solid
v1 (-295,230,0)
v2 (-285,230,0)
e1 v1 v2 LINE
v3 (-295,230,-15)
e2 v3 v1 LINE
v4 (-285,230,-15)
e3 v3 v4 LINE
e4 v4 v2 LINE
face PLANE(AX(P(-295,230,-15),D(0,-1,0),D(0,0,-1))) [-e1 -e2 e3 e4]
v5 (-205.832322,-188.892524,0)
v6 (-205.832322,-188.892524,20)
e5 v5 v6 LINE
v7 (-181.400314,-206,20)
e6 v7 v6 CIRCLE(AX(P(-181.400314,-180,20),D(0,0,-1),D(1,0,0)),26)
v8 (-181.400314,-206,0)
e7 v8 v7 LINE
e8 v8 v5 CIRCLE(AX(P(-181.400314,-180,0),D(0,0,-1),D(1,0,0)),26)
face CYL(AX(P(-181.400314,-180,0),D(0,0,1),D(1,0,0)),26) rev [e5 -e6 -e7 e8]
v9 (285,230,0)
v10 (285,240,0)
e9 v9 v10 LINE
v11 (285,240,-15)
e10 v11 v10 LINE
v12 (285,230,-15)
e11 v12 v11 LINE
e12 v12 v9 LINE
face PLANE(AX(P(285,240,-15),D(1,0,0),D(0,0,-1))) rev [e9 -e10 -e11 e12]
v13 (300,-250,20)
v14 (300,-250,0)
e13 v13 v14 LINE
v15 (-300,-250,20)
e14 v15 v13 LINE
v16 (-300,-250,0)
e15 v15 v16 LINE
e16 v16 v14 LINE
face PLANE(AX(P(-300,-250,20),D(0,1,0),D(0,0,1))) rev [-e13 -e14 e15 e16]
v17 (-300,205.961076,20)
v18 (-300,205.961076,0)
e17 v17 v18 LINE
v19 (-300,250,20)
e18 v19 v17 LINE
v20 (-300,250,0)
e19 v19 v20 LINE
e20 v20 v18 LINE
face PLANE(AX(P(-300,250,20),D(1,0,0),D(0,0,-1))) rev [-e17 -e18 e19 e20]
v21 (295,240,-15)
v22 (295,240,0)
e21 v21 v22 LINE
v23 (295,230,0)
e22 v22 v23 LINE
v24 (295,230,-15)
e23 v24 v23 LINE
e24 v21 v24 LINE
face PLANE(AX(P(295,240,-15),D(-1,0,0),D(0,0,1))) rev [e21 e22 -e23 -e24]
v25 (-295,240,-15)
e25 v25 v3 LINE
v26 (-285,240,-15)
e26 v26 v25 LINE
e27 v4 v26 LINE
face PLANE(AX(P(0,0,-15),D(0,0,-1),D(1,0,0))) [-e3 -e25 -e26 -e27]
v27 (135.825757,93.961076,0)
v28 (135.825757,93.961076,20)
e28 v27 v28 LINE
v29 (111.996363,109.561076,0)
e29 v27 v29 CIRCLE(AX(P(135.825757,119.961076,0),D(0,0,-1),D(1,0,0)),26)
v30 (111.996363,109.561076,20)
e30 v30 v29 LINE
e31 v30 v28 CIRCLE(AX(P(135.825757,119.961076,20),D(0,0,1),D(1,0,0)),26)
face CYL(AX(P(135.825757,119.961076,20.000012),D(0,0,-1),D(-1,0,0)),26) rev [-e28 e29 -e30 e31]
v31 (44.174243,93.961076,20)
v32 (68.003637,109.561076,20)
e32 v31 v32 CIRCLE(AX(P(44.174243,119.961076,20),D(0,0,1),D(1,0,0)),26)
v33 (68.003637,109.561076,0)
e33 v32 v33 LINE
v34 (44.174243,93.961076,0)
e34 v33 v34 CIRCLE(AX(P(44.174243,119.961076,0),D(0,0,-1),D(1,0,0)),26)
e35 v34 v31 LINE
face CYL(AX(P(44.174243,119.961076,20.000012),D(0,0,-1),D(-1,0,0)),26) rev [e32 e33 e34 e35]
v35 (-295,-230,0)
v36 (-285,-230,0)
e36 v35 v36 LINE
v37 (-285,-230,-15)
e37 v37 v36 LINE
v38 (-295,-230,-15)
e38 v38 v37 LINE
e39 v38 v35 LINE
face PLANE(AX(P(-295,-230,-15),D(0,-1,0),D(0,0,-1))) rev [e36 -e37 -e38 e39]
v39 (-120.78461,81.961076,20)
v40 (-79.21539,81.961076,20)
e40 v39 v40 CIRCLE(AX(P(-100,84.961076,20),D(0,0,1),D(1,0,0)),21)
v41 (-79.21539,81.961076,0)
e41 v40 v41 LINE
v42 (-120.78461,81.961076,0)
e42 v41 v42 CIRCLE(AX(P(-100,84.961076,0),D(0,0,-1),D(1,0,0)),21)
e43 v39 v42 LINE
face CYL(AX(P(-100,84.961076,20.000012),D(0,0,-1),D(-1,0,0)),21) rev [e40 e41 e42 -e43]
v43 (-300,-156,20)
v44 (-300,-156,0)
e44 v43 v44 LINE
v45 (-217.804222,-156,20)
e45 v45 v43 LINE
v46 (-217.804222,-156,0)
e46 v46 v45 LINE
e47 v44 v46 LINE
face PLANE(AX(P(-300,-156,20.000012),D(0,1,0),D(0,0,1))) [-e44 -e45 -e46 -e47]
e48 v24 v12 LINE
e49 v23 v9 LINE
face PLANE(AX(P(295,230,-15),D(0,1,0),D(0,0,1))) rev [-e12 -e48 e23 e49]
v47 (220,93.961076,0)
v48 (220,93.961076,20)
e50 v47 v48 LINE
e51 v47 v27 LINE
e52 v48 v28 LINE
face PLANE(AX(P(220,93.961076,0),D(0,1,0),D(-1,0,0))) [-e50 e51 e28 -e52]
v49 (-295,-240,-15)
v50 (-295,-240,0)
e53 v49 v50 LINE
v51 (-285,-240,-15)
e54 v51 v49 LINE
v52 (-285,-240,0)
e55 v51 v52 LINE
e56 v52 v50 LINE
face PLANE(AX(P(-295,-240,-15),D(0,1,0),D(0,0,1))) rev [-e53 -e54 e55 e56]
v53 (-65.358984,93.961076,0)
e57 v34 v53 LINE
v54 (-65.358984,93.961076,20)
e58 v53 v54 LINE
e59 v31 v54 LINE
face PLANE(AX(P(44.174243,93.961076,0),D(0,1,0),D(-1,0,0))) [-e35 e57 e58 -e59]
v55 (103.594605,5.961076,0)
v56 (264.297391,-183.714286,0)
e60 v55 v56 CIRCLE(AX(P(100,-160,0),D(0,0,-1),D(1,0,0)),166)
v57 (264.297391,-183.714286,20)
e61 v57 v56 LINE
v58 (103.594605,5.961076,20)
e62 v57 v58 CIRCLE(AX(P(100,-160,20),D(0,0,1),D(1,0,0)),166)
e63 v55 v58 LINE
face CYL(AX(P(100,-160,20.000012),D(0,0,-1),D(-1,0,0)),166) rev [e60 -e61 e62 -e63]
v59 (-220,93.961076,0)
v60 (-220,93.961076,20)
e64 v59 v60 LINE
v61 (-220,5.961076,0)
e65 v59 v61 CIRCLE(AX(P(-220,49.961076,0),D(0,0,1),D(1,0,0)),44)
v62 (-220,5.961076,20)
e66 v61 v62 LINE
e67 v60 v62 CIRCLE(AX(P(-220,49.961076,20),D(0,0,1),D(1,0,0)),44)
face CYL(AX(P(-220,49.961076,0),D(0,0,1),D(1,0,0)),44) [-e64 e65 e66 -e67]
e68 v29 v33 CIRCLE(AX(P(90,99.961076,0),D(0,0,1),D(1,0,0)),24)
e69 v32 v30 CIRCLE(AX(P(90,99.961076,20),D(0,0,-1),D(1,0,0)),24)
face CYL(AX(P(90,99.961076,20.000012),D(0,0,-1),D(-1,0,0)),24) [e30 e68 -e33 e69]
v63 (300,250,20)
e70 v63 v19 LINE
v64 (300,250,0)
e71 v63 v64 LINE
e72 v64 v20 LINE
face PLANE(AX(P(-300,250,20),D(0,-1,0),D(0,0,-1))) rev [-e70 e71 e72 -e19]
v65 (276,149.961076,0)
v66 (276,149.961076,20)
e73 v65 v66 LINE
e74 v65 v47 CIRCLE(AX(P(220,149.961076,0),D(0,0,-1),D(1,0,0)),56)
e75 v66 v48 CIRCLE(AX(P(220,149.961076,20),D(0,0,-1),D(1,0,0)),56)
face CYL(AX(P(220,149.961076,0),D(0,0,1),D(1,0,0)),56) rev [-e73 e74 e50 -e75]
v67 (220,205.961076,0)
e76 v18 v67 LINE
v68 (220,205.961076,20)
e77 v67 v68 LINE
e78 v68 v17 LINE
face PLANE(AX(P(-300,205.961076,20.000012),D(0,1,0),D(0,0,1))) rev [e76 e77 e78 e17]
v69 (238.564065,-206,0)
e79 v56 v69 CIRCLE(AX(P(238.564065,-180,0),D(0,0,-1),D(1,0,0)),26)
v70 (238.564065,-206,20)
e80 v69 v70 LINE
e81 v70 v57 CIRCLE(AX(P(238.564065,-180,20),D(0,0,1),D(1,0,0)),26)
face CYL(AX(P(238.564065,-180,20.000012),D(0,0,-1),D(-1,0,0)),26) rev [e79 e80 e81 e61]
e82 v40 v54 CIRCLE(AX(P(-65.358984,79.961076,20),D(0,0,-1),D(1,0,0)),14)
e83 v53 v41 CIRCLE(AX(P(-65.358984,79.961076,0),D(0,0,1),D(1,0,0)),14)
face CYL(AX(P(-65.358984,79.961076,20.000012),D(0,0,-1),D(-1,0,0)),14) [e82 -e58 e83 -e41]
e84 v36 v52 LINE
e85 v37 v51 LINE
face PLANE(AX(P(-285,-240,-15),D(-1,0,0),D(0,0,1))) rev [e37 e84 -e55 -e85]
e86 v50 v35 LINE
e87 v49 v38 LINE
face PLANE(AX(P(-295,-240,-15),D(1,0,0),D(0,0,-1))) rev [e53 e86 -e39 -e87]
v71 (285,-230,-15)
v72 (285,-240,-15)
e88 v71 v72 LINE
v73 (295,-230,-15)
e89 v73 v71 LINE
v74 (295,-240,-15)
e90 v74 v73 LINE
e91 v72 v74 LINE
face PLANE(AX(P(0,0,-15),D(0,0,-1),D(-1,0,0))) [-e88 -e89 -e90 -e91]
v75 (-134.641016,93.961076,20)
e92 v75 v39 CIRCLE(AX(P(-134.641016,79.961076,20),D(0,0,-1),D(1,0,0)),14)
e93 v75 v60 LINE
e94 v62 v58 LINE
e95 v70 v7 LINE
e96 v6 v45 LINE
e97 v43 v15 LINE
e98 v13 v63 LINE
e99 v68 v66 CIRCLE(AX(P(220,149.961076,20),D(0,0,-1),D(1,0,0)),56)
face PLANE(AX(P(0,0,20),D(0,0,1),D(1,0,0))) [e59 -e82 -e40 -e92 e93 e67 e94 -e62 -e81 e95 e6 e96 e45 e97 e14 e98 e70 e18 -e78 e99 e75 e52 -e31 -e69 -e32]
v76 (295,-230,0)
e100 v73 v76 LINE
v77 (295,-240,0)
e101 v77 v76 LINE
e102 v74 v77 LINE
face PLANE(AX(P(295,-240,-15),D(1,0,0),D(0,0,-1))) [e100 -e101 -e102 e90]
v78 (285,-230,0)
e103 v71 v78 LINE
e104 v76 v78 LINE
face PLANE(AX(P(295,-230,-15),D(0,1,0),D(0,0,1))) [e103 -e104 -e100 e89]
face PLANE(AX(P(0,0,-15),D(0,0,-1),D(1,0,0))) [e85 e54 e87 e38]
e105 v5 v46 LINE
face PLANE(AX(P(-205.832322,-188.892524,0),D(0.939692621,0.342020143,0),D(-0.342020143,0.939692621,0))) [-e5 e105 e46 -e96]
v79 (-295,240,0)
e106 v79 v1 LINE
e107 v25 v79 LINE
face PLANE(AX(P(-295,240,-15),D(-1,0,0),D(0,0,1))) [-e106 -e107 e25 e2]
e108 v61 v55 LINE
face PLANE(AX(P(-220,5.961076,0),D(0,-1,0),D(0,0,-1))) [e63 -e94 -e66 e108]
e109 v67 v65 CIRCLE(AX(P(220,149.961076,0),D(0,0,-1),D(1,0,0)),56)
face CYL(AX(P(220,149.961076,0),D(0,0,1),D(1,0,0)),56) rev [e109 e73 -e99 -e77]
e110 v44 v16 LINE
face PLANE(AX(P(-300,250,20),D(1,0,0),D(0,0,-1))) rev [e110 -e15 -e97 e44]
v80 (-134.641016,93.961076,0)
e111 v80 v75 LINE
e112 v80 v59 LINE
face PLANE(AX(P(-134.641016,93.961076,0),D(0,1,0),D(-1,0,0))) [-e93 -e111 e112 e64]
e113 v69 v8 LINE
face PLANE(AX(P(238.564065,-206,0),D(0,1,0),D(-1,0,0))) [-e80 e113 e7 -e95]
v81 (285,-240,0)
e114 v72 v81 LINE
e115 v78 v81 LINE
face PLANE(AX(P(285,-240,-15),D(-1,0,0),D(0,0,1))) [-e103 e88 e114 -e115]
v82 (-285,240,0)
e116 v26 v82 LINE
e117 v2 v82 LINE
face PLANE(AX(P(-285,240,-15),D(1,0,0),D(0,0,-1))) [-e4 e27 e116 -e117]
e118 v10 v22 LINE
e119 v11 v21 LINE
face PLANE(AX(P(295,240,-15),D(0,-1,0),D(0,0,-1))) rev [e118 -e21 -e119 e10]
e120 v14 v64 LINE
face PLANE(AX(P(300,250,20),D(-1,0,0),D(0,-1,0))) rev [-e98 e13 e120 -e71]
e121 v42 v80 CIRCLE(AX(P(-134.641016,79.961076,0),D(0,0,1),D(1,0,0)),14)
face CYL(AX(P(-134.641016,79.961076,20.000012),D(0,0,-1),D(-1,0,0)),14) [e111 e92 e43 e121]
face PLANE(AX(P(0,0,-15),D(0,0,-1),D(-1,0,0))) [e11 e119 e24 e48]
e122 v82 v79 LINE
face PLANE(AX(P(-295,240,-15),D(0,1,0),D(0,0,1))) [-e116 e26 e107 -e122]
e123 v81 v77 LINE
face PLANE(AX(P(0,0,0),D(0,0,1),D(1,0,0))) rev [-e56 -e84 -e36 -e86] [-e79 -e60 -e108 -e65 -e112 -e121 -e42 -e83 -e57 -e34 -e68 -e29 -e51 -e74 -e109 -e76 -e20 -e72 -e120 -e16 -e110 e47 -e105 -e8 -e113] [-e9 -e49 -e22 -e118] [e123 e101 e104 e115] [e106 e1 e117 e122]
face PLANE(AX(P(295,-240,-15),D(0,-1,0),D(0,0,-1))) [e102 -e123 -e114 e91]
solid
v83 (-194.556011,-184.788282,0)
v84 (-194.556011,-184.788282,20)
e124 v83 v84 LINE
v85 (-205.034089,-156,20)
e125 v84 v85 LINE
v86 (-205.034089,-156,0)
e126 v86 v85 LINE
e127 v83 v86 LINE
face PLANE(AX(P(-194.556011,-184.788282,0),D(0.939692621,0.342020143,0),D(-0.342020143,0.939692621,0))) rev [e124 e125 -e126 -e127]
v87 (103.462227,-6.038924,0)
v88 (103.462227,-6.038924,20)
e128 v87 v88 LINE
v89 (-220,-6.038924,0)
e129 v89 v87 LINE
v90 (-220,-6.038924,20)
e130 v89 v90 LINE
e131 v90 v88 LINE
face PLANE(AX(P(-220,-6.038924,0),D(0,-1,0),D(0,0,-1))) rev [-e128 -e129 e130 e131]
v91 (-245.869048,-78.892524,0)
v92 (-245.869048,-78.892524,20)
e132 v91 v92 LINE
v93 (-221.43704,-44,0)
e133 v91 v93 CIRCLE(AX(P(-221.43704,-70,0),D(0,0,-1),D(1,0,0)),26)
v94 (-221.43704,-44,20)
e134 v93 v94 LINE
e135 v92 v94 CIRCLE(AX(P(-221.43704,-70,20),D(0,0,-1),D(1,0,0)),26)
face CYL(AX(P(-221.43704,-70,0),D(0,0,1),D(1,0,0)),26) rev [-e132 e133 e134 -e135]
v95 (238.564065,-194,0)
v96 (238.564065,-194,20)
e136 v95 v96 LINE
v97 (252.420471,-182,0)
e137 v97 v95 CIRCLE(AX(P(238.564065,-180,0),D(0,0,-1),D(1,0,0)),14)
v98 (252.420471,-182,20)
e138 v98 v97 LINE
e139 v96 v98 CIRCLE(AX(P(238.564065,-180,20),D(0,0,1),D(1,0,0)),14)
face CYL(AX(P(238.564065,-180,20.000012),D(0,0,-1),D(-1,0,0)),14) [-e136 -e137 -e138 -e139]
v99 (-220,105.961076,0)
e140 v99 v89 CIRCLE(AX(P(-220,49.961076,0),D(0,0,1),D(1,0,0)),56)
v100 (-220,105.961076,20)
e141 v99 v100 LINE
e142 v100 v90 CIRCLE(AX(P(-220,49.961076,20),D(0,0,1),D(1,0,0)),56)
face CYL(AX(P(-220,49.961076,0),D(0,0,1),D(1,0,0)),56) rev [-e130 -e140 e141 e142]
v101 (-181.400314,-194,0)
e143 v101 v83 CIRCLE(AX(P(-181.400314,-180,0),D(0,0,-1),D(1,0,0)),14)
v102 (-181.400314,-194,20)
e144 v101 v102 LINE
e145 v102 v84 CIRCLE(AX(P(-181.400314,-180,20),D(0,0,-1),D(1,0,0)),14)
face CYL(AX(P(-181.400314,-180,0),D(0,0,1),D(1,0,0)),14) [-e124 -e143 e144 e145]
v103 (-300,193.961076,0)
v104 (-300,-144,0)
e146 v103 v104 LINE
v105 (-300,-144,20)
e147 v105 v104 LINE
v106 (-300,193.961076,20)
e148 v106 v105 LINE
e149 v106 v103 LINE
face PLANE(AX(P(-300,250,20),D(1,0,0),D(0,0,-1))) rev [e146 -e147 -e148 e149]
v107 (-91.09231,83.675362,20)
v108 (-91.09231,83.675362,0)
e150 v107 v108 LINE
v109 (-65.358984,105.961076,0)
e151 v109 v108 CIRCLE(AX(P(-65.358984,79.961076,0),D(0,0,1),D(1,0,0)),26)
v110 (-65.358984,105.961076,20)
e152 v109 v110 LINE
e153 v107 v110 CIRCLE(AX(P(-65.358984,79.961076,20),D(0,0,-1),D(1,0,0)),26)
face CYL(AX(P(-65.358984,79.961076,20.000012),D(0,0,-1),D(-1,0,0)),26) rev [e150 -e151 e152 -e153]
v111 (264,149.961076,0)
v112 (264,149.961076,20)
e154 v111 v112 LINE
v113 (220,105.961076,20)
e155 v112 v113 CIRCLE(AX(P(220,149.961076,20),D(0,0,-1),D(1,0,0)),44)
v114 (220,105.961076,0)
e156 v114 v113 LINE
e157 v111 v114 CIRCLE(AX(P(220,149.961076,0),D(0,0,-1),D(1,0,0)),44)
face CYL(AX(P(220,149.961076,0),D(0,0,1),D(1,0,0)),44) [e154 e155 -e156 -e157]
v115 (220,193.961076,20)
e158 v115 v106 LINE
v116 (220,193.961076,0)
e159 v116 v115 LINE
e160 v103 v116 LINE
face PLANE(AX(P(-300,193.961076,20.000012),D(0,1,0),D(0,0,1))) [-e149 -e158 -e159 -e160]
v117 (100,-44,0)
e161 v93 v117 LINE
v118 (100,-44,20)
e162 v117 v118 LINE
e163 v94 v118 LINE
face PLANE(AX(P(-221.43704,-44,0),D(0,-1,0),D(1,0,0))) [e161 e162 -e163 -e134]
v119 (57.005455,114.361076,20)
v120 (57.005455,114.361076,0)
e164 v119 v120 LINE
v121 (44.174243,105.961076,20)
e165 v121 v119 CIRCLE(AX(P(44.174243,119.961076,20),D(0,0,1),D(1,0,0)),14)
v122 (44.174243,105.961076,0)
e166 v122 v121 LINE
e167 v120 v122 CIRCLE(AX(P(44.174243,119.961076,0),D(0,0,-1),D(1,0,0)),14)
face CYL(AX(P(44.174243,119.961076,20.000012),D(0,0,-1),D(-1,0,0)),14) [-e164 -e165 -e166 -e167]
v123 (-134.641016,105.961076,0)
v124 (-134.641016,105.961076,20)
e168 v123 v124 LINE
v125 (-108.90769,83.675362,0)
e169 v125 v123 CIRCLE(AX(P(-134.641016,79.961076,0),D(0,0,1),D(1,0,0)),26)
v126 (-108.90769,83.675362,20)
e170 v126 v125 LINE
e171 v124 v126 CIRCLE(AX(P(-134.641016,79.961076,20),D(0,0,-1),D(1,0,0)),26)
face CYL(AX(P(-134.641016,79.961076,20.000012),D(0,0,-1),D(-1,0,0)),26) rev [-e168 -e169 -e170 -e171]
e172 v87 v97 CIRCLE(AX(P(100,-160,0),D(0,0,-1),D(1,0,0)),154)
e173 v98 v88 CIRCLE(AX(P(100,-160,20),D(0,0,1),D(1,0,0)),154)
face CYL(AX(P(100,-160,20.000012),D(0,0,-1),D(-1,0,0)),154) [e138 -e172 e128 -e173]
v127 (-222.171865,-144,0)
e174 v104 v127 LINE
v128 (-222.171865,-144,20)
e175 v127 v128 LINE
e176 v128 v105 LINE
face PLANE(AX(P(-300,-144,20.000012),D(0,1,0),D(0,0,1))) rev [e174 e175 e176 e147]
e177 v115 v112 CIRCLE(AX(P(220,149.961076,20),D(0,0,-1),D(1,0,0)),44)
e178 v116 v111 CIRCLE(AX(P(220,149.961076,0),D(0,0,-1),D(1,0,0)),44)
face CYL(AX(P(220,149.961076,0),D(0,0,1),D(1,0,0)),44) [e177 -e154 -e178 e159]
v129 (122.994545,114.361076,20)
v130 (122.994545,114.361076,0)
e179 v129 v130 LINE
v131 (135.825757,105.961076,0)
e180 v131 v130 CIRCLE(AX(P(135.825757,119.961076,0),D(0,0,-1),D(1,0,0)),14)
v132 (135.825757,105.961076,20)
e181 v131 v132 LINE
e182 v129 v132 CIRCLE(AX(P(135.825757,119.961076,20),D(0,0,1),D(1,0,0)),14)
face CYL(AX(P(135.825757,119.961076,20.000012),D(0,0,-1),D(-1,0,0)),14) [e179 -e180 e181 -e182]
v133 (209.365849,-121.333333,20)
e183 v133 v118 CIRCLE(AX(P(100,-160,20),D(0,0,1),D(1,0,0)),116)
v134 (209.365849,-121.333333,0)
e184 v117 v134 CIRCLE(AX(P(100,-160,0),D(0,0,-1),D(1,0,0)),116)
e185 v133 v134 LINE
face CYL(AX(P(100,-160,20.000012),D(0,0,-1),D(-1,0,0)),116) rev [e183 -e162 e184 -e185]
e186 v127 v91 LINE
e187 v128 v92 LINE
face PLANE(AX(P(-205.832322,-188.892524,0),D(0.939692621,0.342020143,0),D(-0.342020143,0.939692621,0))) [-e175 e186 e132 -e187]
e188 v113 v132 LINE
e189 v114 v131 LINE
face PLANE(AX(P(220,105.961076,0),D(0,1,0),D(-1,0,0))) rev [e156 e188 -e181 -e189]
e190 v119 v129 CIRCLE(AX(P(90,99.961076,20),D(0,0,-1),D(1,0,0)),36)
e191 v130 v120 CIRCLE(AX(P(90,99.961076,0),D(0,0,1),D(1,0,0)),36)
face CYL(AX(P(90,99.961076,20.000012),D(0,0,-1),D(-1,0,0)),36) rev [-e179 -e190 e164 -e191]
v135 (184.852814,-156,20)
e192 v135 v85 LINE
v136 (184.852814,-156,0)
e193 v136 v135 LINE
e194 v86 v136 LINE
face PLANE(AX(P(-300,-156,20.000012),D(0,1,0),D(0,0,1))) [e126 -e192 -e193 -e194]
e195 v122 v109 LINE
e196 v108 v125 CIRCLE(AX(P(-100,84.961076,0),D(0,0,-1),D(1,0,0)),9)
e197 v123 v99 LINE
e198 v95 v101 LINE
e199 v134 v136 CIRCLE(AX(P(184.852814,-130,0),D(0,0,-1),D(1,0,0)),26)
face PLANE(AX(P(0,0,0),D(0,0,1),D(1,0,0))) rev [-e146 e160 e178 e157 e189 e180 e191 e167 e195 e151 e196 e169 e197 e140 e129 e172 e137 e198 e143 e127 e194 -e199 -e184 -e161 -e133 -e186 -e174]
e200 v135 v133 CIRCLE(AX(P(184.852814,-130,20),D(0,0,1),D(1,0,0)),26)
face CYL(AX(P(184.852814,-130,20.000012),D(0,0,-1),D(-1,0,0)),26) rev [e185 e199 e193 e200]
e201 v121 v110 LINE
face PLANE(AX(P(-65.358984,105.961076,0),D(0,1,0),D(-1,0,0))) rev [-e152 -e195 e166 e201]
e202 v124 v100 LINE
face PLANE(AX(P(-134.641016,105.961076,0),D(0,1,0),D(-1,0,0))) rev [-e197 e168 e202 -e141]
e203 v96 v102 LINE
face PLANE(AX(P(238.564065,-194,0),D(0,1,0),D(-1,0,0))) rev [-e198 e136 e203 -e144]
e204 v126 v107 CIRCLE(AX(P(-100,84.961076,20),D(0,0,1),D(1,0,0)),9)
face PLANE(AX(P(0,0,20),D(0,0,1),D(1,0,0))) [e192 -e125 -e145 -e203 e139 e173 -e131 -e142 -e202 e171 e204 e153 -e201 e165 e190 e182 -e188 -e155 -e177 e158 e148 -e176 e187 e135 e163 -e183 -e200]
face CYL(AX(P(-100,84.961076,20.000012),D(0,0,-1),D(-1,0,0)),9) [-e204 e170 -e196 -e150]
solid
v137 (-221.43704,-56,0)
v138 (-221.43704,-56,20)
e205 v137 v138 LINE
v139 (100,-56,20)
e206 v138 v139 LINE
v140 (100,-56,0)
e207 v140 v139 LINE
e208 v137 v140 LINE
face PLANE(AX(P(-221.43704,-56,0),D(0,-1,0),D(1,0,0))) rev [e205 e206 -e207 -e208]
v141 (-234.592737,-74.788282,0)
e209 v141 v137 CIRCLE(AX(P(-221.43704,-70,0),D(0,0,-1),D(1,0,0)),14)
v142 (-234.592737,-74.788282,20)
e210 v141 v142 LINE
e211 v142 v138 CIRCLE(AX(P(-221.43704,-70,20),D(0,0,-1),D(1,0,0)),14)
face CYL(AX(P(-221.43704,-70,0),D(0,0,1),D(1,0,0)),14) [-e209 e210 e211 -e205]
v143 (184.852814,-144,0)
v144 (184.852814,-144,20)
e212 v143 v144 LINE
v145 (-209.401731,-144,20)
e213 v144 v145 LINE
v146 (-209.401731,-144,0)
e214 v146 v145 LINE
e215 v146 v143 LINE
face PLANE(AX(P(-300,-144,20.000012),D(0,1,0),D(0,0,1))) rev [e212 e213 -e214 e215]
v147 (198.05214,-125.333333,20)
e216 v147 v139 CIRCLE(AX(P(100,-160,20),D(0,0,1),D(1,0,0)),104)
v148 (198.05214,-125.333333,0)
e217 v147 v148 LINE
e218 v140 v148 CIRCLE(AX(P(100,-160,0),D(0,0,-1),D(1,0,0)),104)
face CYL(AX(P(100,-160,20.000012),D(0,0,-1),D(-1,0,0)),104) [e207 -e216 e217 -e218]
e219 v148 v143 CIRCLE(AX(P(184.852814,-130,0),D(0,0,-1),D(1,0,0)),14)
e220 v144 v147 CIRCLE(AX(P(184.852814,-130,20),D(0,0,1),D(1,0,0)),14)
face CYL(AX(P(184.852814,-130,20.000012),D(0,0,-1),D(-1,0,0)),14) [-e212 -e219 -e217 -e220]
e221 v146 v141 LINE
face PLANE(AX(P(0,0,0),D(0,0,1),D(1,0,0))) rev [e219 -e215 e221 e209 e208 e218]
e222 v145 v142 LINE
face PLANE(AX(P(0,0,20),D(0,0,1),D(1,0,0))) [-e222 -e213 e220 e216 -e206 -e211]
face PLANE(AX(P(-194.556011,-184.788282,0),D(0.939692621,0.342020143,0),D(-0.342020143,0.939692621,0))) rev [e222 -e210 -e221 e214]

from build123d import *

# Parameters (mm, degrees)
SKETCH1_W                    = 600
SKETCH1_H                    = 500
BOSS_EXTRUDE1_DEPTH          = 20
CUT_EXTRUDE_THIN1_DEPTH      = 392.02429592
CUT_EXTRUDE_THIN1_DEPTH_BACK = 20
CUT_EXTRUDE_THIN2_DEPTH      = 392.02429592
CUT_EXTRUDE_THIN2_DEPTH_BACK = 20
SKETCH3_W                    = 484.852813742
SKETCH3_H                    = 12
SKETCH4_W                    = 10
SKETCH4_H                    = 10
BOSS_EXTRUDE2_DEPTH          = 15
MIRROR2_COPY_1_SKETCH_W      = 10
MIRROR2_COPY_1_SKETCH_H      = 10
MIRROR2_COPY_1_DEPTH         = 15


with BuildPart() as part:
    # Sketch1 → Boss-Extrude1 (new body)
    with BuildSketch(Plane.XY):
        Rectangle(SKETCH1_W, SKETCH1_H)
    extrude(amount=BOSS_EXTRUDE1_DEPTH)

    # Sketch2 → Cut-Extrude-Thin1 (cut, two sides: drawn at the far end of the back side and taken through both)
    with BuildSketch(Plane.XY.offset(20).offset(-CUT_EXTRUDE_THIN1_DEPTH_BACK)):
        with BuildLine():
            Line((-300, 193.961076205), (220, 193.961076205))
            ThreePointArc((220, 193.961076205), (264, 149.961076205), (220, 105.961076205))
            Line((220, 105.961076205), (135.82575695, 105.961076205))
            ThreePointArc((135.82575695, 105.961076205), (128.157641144, 108.247835834), (122.994545004, 114.361076205))
            ThreePointArc((122.994545004, 114.361076205), (90, 135.961076205), (57.005454996, 114.361076205))
            ThreePointArc((57.005454996, 114.361076205), (51.842358856, 108.247835834), (44.17424305, 105.961076205))
            Line((44.17424305, 105.961076205), (-2.040587873, 105.961076205))
            Line((-2.040587873, 105.961076205), (-65.358983849, 105.961076205))
            ThreePointArc((-65.358983849, 105.961076205), (-82.379979287, 99.615228802), (-91.092310133, 83.675361919))
            ThreePointArc((-91.092310133, 83.675361919), (-100, 75.961076205), (-108.907689867, 83.675361919))
            ThreePointArc((-108.907689867, 83.675361919), (-117.620020713, 99.615228802), (-134.641016151, 105.961076205))
            Line((-134.641016151, 105.961076205), (-220, 105.961076205))
            ThreePointArc((-220, 105.961076205), (-276, 49.961076205), (-220, -6.038923795))
            Line((-220, -6.038923795), (103.462226705, -6.038923795))
            ThreePointArc((103.462226705, -6.038923795), (217.539052876, -60.498386701), (252.420471066, -182))
            ThreePointArc((252.420471066, -182), (247.729215995, -190.583005244), (238.564064606, -194))
            Line((238.564064606, -194), (-181.400314096, -194))
            ThreePointArc((-181.400314096, -194), (-189.430384205, -191.46812862), (-194.556010787, -184.788282007))
            Line((-194.556010787, -184.788282007), (-234.592736556, -74.788282007))
            ThreePointArc((-234.592736556, -74.788282007), (-232.905168485, -61.969929891), (-221.437039865, -56))
            Line((-221.437039865, -56), (100, -56))
            ThreePointArc((100, -56), (160.044427996, -75.084355584), (198.052140325, -125.333333333))
            ThreePointArc((198.052140325, -125.333333333), (196.283765875, -138.082903769), (184.852813742, -144))
            Line((184.852813742, -144), (184.852813742, -156))
            ThreePointArc((184.852813742, -156), (206.081724847, -145.011106999), (209.365848824, -121.333333333))
            ThreePointArc((209.365848824, -121.333333333), (166.972631226, -65.286396612), (100, -44))
            Line((100, -44), (-221.437039865, -44))
            ThreePointArc((-221.437039865, -44), (-242.734993017, -55.087012655), (-245.869048006, -78.892523726))
            Line((-245.869048006, -78.892523726), (-205.832322236, -188.892523726))
            ThreePointArc((-205.832322236, -188.892523726), (-196.313301441, -201.297953152), (-181.400314096, -206))
            Line((-181.400314096, -206), (238.564064606, -206))
            ThreePointArc((238.564064606, -206), (255.585060044, -199.654152596), (264.297390889, -183.714285714))
            ThreePointArc((264.297390889, -183.714285714), (226.653528564, -52.692573871), (103.594604963, 5.961076205))
            Line((103.594604963, 5.961076205), (-220, 5.961076205))
            ThreePointArc((-220, 5.961076205), (-264, 49.961076205), (-220, 93.961076205))
            Line((-220, 93.961076205), (-134.641016151, 93.961076205))
            ThreePointArc((-134.641016151, 93.961076205), (-125.475864761, 90.544081449), (-120.784609691, 81.961076205))
            ThreePointArc((-120.784609691, 81.961076205), (-100, 63.961076205), (-79.215390309, 81.961076205))
            ThreePointArc((-79.215390309, 81.961076205), (-74.524135239, 90.544081449), (-65.358983849, 93.961076205))
            Line((-65.358983849, 93.961076205), (-2.040587873, 93.961076205))
            Line((-2.040587873, 93.961076205), (44.17424305, 93.961076205))
            ThreePointArc((44.17424305, 93.961076205), (58.415029546, 98.207915515), (68.003636664, 109.561076205))
            ThreePointArc((68.003636664, 109.561076205), (90, 123.961076205), (111.996363336, 109.561076205))
            ThreePointArc((111.996363336, 109.561076205), (121.584970454, 98.207915515), (135.82575695, 93.961076205))
            Line((135.82575695, 93.961076205), (220, 93.961076205))
            ThreePointArc((220, 93.961076205), (276, 149.961076205), (220, 205.961076205))
            Line((220, 205.961076205), (-300, 205.961076205))
            Line((-300, 205.961076205), (-300, 193.961076205))
        make_face()
    extrude(amount=CUT_EXTRUDE_THIN1_DEPTH + CUT_EXTRUDE_THIN1_DEPTH_BACK, mode=Mode.SUBTRACT)

    # Sketch3 → Cut-Extrude-Thin2 (cut, two sides: drawn at the far end of the back side and taken through both)
    with BuildSketch(Plane.XY.offset(20).offset(-CUT_EXTRUDE_THIN2_DEPTH_BACK)):
        with Locations((-57.573593129, -150)):
            Rectangle(SKETCH3_W, SKETCH3_H)
    extrude(amount=CUT_EXTRUDE_THIN2_DEPTH + CUT_EXTRUDE_THIN2_DEPTH_BACK, mode=Mode.SUBTRACT)


with BuildPart() as cut_extrude_thin2_piece_1:
    # of the separate pieces the step leaves, piece 1, a body of its own (cut_extrude_thin2_pieces)
    add(part.part.solids().sort_by_distance((-300, 250, 0))[0])

    # Sketch4 → Boss-Extrude2 (add)
    with BuildSketch(Plane(origin=(0, 0, 0), x_dir=(-1, 0, 0), z_dir=(0, 0, -1))):
        with Locations((-290, 235)):
            Rectangle(SKETCH4_W, SKETCH4_H)
    boss_extrude2 = extrude(amount=BOSS_EXTRUDE2_DEPTH)

    # Mirror1: Boss-Extrude2 across plane
    add(boss_extrude2.mirror(Plane(origin=(0, 0, 0), x_dir=(0, 0, 1), z_dir=(1, 0, 0))))

    # Mirror2: Boss-Extrude2 across plane
    add(boss_extrude2.mirror(Plane.ZX))

    # Mirror2 copy 1 sketch → Mirror2 copy 1 (add)
    with BuildSketch(Plane(origin=(0, 0, 0), x_dir=(1, 0, 0), z_dir=(0, 0, -1))):
        with Locations((-290, 235)):
            Rectangle(MIRROR2_COPY_1_SKETCH_W, MIRROR2_COPY_1_SKETCH_H)
    extrude(amount=MIRROR2_COPY_1_DEPTH)


with BuildPart() as cut_extrude_thin2_piece_2:
    # of the separate pieces the step leaves, piece 2, a body of its own (cut_extrude_thin2_pieces)
    add(part.part.solids().sort_by_distance((-222.171864614, -144, 0))[0])


with BuildPart() as cut_extrude_thin2_piece_3:
    # of the separate pieces the step leaves, piece 3, a body of its own (cut_extrude_thin2_pieces)
    add(part.part.solids().sort_by_distance((198.052140325, -125.333333333, 0))[0])


solid = Compound([cut_extrude_thin2_piece_1.part, cut_extrude_thin2_piece_2.part, cut_extrude_thin2_piece_3.part])
